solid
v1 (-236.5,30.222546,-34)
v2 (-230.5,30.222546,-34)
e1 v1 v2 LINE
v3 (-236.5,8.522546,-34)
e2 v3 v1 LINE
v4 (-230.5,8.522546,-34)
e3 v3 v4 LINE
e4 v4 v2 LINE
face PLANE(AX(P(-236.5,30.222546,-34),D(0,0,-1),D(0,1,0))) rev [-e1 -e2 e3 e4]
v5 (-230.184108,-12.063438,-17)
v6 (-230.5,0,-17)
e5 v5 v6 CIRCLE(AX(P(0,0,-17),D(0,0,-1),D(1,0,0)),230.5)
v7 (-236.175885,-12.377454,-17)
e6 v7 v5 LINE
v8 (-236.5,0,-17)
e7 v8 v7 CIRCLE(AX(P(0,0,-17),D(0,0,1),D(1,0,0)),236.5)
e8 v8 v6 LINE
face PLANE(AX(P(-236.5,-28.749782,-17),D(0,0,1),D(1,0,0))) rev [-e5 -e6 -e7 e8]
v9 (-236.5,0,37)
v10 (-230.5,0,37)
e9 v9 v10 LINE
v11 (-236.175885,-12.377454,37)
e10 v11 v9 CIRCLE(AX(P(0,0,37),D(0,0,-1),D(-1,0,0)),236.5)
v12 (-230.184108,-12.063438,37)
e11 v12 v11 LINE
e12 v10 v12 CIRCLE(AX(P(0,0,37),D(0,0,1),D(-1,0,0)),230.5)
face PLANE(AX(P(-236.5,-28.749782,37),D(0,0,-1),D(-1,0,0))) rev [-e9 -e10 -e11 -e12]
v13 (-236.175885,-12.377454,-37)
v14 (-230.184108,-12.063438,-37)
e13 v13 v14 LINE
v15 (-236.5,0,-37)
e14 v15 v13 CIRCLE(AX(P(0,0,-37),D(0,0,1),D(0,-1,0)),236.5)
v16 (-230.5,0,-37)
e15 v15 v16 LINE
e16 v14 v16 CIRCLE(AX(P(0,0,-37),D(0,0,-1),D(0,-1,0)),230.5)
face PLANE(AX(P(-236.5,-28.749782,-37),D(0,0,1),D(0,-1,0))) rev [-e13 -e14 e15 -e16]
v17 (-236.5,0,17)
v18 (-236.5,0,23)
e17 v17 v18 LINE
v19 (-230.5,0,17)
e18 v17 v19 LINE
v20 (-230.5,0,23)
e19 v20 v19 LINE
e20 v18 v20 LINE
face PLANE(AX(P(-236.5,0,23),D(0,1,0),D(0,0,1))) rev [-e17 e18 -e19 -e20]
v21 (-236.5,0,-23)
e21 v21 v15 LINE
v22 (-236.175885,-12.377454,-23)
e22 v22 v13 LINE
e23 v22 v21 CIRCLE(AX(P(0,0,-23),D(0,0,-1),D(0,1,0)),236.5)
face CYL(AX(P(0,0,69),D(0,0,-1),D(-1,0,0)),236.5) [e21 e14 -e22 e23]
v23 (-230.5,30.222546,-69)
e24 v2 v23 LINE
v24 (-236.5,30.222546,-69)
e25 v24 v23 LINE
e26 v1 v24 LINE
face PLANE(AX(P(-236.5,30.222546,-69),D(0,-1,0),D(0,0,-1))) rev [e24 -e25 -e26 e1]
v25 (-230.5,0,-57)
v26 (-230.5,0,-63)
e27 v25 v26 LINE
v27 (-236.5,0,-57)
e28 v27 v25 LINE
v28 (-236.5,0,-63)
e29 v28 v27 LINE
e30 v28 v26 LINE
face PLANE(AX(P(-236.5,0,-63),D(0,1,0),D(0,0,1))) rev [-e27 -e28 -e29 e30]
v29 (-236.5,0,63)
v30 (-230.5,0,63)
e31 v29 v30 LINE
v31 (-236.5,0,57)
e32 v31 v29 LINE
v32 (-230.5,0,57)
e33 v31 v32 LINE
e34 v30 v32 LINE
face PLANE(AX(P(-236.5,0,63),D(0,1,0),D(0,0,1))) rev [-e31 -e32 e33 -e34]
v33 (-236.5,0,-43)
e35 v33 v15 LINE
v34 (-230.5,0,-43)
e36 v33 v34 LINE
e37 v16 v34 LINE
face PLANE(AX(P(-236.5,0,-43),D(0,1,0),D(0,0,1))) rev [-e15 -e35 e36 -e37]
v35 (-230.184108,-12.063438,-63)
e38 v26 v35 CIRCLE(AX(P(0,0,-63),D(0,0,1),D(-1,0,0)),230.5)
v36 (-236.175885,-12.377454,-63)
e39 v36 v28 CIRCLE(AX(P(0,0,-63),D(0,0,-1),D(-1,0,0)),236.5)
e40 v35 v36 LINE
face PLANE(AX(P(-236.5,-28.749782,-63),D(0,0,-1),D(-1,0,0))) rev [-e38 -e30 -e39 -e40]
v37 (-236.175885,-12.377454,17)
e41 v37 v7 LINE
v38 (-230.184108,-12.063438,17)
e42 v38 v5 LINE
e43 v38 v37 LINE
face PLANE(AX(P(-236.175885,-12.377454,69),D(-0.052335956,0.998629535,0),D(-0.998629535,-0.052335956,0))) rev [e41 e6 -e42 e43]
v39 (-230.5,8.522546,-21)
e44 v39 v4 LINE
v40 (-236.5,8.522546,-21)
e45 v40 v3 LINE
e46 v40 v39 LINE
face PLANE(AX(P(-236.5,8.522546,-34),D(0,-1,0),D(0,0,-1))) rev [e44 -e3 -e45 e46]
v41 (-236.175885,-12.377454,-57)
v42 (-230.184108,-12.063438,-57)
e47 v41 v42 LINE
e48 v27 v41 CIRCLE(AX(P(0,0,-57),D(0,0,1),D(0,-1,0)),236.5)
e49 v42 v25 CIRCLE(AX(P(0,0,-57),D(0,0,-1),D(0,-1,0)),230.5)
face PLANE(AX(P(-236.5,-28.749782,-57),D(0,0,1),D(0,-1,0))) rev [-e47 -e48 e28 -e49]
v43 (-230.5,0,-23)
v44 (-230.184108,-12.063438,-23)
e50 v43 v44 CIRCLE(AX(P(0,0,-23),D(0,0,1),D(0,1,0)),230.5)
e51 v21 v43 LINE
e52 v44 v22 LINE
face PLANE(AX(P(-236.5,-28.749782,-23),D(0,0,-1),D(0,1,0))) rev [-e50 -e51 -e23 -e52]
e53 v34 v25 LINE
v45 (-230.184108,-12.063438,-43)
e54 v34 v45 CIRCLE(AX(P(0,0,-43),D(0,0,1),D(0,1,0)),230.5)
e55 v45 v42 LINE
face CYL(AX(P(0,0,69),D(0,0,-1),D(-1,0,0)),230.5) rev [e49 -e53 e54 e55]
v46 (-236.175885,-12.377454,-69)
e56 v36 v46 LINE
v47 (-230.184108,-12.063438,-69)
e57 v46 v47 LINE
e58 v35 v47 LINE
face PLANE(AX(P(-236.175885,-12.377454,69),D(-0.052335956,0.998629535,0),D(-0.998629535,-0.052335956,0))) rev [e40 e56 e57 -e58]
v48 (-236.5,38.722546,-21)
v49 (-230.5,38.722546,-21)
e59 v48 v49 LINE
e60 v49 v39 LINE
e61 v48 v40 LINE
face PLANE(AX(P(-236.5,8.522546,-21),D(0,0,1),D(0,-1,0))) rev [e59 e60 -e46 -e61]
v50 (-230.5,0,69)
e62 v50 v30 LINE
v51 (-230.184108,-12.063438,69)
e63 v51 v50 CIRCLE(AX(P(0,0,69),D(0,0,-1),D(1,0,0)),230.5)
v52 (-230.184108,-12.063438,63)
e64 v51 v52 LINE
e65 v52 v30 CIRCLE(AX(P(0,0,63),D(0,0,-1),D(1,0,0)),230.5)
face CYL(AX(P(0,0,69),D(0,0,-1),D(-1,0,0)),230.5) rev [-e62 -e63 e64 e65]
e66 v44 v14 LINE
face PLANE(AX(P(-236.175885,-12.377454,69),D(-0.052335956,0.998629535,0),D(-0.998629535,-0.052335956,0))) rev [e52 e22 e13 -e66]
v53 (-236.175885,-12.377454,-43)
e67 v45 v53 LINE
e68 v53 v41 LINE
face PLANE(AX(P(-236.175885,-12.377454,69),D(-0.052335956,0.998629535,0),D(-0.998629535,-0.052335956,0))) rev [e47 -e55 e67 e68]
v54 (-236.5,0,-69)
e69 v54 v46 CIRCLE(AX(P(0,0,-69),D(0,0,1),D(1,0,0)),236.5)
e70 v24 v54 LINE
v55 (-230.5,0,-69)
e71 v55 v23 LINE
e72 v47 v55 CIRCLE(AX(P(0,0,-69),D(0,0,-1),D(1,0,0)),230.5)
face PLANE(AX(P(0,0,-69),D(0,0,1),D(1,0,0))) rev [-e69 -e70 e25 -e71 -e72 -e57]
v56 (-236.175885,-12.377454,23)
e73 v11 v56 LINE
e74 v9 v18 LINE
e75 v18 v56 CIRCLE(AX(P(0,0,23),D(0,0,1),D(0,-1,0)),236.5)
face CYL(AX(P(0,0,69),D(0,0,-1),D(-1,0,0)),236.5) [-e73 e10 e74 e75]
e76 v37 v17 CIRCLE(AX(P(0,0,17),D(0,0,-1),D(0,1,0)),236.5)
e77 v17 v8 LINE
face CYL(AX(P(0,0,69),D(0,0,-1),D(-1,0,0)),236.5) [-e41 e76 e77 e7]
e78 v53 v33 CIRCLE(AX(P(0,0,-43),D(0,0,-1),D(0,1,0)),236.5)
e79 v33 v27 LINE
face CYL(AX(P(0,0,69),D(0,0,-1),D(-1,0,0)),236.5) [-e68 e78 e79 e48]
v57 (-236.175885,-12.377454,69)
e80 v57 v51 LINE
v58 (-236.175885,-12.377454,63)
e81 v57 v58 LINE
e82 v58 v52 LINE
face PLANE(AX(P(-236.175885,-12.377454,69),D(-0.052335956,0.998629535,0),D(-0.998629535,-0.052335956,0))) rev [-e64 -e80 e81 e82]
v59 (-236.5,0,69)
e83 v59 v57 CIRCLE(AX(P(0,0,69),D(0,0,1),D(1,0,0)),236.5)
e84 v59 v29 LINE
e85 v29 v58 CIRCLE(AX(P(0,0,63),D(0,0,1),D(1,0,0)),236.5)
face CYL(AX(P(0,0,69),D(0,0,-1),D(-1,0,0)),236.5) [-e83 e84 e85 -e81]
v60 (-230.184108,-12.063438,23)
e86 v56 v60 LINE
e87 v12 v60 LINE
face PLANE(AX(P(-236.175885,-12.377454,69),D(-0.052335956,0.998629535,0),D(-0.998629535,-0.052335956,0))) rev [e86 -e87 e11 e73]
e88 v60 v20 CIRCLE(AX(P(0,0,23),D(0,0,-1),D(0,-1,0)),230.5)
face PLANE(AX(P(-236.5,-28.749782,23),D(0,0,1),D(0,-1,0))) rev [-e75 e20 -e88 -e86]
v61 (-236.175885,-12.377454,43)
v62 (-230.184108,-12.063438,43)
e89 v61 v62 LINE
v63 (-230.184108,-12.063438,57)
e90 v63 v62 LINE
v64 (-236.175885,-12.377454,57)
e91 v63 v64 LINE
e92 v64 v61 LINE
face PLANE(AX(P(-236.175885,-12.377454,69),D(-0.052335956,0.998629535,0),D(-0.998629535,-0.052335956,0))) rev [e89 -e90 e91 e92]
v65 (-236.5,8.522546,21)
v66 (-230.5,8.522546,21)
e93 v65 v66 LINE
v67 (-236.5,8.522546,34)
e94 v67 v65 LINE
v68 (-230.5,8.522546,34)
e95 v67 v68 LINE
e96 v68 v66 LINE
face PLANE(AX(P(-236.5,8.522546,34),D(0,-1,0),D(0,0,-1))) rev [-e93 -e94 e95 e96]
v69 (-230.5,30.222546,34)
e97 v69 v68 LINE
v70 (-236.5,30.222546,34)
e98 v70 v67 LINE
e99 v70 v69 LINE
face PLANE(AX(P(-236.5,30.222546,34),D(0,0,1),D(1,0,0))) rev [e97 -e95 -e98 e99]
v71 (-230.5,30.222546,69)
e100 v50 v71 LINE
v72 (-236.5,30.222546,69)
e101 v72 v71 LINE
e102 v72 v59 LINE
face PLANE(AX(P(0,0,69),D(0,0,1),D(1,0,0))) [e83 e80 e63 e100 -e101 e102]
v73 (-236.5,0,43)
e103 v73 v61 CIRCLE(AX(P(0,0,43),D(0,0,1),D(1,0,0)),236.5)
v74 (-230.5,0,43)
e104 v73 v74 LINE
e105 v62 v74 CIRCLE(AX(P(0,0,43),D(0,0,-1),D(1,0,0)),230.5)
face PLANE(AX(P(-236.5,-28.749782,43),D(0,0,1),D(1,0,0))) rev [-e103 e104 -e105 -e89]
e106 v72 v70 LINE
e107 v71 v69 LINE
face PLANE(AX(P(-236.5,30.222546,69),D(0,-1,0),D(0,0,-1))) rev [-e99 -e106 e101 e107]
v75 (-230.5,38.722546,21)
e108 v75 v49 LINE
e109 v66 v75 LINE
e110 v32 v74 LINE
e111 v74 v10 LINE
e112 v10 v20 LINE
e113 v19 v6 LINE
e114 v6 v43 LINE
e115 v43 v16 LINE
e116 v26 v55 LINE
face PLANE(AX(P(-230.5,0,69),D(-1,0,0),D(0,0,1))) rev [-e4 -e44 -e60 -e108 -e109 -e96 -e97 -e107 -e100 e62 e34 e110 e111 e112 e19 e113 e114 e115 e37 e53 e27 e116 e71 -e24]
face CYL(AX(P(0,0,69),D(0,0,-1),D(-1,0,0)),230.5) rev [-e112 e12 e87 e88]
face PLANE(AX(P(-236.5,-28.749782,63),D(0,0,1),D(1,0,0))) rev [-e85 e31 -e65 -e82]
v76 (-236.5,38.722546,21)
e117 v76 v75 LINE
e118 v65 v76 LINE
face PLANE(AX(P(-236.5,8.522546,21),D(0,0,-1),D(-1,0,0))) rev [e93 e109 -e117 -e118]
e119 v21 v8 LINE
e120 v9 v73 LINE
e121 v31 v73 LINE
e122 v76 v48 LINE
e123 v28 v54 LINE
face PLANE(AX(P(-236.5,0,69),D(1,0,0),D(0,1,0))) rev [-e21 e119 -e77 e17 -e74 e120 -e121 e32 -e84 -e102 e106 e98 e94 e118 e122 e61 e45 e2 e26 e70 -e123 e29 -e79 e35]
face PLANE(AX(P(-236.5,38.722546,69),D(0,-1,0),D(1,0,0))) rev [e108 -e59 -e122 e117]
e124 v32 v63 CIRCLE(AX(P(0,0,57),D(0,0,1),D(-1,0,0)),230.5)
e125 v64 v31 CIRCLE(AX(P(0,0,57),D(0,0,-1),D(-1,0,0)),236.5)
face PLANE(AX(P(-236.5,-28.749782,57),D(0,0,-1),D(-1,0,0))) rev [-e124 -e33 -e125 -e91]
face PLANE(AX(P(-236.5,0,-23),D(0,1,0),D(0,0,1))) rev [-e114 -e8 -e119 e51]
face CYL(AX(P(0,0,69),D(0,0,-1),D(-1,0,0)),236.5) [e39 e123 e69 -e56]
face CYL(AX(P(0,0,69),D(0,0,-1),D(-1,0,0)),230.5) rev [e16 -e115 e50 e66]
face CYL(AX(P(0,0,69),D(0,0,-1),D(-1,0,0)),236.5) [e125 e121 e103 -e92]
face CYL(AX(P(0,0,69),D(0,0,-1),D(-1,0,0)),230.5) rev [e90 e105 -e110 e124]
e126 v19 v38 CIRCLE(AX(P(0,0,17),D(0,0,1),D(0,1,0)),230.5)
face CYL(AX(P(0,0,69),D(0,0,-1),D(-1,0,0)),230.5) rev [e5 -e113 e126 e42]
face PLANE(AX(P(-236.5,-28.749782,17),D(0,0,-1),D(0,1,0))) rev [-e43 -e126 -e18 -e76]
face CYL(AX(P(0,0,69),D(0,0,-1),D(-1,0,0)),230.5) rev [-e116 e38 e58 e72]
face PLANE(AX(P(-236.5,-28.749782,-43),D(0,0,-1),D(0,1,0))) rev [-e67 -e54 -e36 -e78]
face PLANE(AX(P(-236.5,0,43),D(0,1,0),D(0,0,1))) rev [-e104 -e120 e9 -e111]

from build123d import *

# Parameters (mm, degrees)
BOSS_EXTRUDE1_DEPTH = 69
SKETCH5_W           = 6
SKETCH5_H           = 28.749782116
CUT_EXTRUDE5_DEPTH  = 250.384613791
CUT_EXTRUDE1_DEPTH  = 80.350082519


with BuildPart() as part:
    # Sketch1 → Boss-Extrude1 (new, symmetric)
    with BuildSketch(Plane.XY):
        with BuildLine():
            Line((-236.175884969, -12.377453651), (-230.184107761, -12.063437914))
            ThreePointArc((-230.184107761, -12.063437914), (-230.421013407, -6.033786585), (-230.5, 0))
            Line((-230.5, 0), (-230.5, 38.722546349))
            Line((-230.5, 38.722546349), (-236.5, 38.722546349))
            Line((-236.5, 38.722546349), (-236.5, 0))
            ThreePointArc((-236.5, 0), (-236.418957357, -6.190848275), (-236.175884969, -12.377453651))
        make_face()
    extrude(amount=BOSS_EXTRUDE1_DEPTH, both=True)

    # Sketch5 → Cut-Extrude5 (cut, through all)
    with BuildSketch(Plane(origin=(0, 0, 0), x_dir=(0, 0, -1), z_dir=(1, 0, 0))):
        with Locations((-60, -14.374891058)):
            Rectangle(SKETCH5_W, SKETCH5_H)
        with Locations((-40, -14.374891058)):
            Rectangle(SKETCH5_W, SKETCH5_H)
        with Locations((-20, -14.374891058)):
            Rectangle(SKETCH5_W, SKETCH5_H)
        with Locations((20, -14.374891058)):
            Rectangle(SKETCH5_W, SKETCH5_H)
        with Locations((40, -14.374891058)):
            Rectangle(SKETCH5_W, SKETCH5_H)
        with Locations((60, -14.374891058)):
            Rectangle(SKETCH5_W, SKETCH5_H)
    extrude(amount=-CUT_EXTRUDE5_DEPTH, mode=Mode.SUBTRACT)

    # Sketch3 → Cut-Extrude1 (cut, through all)
    with BuildSketch(Plane(origin=(-230.5, 0, 0), x_dir=(0, 0, -1), z_dir=(1, 0, 0))):
        Polygon((-69, 30.222546349), (-34, 30.222546349), (-34, 8.522546349), (-21, 8.522546349), (-21, 38.722546349), (-69, 38.722546349), align=None)
        Polygon((21, 8.522546349), (21, 38.722546349), (69, 38.722546349), (69, 30.222546349), (34, 30.222546349), (34, 8.522546349), align=None)
    extrude(amount=-CUT_EXTRUDE1_DEPTH, mode=Mode.SUBTRACT)


solid = part.part
